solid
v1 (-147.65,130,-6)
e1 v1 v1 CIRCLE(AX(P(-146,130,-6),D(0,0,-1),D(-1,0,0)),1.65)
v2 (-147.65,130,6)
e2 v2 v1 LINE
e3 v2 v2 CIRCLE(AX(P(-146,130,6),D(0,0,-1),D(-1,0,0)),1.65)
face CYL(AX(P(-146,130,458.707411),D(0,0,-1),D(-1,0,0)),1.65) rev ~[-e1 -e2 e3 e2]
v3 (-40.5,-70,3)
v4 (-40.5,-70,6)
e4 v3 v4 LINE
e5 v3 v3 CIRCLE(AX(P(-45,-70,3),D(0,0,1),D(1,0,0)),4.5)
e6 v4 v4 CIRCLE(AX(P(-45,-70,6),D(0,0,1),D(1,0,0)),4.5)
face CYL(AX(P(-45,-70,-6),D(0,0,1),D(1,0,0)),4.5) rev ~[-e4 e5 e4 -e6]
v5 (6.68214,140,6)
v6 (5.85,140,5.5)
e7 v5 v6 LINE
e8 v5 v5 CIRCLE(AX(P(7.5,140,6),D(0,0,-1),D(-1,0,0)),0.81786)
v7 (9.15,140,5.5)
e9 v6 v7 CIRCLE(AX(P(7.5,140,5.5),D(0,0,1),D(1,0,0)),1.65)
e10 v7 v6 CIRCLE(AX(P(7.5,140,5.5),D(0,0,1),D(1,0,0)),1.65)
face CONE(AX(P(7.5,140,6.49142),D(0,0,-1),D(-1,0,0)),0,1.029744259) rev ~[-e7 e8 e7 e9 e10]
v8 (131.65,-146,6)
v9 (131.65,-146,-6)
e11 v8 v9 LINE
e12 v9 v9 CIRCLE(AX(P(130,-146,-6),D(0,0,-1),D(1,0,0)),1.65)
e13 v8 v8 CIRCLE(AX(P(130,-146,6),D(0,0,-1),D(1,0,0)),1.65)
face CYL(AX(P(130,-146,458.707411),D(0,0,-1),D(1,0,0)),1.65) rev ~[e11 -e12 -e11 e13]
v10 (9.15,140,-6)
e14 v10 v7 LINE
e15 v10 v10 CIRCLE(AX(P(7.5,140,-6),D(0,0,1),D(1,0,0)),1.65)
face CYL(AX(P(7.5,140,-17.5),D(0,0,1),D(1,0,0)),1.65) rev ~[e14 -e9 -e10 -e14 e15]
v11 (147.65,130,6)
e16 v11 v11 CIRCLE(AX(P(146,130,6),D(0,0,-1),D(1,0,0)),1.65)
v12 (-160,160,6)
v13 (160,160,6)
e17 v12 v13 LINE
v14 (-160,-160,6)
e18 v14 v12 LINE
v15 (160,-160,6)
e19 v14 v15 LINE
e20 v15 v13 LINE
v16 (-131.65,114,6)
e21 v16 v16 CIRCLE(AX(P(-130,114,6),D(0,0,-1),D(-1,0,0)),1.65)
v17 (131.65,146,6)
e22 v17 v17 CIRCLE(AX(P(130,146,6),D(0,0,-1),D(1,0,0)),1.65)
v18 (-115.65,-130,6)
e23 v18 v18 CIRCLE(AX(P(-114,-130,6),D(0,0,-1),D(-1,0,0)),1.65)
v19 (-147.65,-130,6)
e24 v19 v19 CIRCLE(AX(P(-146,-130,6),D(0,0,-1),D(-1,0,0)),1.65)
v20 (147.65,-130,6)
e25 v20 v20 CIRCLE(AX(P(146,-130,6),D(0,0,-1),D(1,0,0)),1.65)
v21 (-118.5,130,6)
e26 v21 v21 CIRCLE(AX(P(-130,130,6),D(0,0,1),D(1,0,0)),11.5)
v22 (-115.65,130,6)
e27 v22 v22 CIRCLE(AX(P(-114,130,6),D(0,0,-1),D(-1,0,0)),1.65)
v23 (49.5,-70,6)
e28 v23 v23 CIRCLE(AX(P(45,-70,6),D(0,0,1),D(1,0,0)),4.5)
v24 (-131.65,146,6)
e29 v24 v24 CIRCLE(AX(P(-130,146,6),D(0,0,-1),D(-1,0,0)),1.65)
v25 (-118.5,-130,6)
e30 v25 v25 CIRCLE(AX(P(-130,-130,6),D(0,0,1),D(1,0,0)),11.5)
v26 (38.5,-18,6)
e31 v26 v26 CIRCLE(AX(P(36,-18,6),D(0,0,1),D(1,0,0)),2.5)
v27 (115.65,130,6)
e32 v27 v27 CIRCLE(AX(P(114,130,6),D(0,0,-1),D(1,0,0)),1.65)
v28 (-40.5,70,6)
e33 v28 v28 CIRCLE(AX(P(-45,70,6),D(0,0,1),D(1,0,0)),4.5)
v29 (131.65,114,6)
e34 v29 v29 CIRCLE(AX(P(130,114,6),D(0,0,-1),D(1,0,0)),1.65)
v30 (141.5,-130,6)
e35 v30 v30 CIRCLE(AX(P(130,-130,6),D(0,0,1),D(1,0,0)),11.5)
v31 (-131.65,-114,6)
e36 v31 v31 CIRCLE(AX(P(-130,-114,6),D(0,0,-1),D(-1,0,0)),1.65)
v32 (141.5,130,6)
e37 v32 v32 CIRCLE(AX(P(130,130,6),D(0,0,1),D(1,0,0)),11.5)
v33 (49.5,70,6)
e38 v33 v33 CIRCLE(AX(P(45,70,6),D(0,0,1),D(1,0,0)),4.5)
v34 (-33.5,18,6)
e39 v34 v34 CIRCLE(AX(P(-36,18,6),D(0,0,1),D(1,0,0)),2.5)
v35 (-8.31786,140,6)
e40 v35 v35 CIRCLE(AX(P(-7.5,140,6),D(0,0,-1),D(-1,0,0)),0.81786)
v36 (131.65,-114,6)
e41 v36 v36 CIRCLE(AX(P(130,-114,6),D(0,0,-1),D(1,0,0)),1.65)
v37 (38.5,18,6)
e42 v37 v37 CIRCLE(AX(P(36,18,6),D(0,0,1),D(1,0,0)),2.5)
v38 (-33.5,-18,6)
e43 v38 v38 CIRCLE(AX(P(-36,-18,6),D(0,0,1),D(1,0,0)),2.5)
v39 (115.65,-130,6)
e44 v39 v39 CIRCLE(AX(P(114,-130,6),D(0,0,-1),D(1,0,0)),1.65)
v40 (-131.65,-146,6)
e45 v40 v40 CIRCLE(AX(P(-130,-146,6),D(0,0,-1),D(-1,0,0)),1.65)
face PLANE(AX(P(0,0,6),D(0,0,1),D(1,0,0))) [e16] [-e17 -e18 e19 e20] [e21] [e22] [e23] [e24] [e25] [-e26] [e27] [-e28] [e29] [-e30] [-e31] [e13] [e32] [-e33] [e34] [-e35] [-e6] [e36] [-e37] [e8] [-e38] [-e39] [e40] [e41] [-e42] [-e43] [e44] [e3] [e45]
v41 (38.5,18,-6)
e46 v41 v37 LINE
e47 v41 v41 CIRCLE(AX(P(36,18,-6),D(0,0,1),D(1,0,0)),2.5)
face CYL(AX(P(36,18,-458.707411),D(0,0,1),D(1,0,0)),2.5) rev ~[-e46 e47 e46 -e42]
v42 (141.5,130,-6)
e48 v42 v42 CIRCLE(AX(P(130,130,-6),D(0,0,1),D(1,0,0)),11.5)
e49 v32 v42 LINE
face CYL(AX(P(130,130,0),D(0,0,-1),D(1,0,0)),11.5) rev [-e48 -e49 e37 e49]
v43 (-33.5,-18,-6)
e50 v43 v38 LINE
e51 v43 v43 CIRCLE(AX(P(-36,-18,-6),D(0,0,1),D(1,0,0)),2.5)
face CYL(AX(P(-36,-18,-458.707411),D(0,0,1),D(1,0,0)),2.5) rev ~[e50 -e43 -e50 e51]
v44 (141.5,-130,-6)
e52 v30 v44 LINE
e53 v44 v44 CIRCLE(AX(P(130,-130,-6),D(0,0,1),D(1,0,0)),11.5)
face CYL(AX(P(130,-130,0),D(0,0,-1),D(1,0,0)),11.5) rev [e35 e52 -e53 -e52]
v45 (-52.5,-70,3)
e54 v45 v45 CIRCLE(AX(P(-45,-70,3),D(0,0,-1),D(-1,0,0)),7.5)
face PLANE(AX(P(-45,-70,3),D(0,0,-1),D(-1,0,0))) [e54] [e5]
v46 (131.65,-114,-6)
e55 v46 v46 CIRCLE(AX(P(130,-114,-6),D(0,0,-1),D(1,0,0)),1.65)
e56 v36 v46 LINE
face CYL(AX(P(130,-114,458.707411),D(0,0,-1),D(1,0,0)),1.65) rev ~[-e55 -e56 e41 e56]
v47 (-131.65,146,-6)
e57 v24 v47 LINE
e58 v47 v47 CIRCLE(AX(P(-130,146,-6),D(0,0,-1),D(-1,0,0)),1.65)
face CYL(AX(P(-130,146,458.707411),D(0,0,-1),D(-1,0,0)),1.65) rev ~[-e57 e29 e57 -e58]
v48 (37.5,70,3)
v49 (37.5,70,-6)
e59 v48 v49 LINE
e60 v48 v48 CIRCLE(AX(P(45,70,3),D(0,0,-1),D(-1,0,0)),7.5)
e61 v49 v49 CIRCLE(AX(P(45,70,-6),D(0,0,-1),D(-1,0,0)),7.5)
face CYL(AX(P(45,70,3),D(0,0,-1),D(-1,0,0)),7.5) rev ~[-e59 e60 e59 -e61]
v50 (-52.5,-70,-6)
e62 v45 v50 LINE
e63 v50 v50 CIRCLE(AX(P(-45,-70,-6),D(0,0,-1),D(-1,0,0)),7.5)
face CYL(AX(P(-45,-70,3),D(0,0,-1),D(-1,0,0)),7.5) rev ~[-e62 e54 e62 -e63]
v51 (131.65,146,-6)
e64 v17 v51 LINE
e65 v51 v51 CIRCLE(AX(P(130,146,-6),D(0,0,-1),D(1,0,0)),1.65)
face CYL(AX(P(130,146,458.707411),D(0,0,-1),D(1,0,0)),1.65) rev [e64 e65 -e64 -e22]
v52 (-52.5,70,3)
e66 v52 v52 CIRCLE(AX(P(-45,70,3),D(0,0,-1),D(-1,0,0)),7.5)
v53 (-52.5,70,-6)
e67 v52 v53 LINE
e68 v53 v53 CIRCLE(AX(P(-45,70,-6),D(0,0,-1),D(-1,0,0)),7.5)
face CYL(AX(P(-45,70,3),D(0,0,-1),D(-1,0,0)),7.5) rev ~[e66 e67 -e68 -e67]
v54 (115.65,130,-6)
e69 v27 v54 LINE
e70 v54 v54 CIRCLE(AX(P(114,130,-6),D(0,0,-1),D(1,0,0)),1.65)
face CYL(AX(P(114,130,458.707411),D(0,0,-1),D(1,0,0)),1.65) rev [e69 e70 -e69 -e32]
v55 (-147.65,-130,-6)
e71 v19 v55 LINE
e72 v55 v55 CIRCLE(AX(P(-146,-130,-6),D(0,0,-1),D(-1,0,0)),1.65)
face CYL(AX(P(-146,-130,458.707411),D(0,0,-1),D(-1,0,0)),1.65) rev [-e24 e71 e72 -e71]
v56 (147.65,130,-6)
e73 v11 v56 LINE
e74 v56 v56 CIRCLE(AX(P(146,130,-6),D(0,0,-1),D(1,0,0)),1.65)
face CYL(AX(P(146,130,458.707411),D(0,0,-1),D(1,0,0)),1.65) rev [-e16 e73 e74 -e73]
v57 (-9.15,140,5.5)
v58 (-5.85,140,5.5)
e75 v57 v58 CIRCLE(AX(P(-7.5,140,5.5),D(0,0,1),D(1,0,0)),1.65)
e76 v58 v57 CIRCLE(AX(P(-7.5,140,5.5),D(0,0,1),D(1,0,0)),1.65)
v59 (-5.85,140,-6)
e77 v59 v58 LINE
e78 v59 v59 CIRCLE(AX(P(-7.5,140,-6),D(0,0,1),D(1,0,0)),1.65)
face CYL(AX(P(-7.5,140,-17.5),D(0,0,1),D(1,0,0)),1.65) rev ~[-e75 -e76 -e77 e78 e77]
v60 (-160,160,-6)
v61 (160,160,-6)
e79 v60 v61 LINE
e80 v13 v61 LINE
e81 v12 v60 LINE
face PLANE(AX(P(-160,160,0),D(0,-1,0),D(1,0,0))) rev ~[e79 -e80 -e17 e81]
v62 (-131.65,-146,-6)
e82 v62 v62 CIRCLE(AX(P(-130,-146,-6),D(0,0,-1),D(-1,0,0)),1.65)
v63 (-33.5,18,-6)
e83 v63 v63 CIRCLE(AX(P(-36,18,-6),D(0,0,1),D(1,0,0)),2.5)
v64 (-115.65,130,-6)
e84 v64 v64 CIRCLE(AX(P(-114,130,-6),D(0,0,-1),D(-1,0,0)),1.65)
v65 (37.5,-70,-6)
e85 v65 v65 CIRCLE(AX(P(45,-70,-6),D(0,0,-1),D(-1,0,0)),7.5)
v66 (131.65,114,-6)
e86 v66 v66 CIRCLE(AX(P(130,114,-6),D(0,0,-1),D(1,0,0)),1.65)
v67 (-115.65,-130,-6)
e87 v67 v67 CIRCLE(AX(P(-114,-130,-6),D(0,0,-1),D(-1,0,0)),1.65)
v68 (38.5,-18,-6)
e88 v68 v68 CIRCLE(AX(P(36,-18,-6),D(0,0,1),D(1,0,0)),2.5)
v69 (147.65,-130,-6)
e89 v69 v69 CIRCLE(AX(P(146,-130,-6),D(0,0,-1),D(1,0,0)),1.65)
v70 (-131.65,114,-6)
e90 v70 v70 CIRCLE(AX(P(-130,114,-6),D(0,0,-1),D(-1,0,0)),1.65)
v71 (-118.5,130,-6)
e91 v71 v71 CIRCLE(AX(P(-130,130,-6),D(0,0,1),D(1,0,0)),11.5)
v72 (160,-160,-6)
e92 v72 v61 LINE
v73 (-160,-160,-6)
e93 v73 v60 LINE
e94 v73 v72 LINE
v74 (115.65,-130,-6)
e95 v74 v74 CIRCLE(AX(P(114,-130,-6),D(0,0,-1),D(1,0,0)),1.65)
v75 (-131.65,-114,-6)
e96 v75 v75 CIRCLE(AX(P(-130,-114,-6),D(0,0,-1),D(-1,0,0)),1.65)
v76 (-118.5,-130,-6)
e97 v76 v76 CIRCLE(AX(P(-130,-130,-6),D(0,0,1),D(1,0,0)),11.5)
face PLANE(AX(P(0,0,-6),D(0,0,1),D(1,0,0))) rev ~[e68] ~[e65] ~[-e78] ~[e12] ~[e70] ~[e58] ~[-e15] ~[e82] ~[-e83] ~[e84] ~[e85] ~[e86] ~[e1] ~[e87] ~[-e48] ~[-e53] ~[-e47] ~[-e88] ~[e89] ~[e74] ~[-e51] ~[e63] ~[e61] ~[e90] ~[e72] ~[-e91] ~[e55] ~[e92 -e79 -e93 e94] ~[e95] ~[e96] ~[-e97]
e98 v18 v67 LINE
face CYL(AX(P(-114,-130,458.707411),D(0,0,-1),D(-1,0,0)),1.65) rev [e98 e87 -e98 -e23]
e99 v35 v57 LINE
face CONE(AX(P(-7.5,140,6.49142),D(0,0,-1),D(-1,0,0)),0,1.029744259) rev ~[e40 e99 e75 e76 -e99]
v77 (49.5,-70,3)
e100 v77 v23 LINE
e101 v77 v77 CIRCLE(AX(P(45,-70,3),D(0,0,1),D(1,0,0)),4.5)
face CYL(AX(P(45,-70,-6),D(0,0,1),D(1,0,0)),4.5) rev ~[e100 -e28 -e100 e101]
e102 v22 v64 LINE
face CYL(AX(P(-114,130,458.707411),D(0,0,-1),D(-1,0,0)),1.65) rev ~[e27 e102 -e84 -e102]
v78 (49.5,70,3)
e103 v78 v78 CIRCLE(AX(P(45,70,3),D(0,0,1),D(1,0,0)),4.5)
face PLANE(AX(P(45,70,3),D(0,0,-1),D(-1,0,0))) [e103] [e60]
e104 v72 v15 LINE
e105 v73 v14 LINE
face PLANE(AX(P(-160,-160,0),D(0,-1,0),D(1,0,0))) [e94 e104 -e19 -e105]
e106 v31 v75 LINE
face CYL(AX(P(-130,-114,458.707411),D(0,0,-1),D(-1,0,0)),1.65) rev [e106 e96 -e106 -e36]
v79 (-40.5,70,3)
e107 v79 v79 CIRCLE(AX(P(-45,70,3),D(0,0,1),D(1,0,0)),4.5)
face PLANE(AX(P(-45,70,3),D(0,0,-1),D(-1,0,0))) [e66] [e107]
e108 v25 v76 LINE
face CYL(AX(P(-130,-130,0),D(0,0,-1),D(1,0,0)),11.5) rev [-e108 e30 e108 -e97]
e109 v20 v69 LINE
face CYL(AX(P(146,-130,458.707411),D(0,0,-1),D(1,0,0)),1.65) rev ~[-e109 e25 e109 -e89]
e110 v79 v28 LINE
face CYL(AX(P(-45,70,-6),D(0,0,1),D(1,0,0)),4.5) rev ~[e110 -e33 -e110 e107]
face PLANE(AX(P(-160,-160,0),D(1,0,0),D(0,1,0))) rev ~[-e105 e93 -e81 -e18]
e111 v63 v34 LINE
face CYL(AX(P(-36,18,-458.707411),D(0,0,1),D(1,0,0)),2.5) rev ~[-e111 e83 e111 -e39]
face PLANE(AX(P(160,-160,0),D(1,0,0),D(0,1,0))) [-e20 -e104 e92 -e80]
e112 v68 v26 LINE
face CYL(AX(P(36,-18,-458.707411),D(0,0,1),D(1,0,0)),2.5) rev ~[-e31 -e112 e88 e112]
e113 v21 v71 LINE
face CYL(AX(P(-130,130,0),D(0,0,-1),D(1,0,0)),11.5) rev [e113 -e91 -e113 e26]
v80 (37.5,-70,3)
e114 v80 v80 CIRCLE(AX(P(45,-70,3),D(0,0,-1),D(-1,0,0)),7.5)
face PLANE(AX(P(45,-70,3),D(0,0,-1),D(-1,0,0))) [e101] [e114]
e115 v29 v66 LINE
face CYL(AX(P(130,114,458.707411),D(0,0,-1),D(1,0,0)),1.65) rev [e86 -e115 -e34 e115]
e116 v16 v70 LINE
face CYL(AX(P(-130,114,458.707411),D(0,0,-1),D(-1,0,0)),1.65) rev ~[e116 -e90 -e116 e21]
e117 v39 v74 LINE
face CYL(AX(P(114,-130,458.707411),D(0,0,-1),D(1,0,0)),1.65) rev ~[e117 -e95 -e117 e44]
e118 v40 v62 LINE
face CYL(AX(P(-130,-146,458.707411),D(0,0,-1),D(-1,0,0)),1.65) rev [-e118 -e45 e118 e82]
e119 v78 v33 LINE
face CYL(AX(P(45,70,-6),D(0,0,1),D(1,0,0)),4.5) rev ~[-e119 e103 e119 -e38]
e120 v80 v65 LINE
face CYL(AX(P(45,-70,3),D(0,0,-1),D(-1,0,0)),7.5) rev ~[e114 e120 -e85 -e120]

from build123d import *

# Parameters (mm, degrees)
SKETCH_1_W                = 320
SKETCH_1_H                = 320
SKETCH_1_R                = 11.5
EXTRUDE_1_DEPTH           = 6
HOLE_WIZARD_M6_1_D        = 5
HOLE_WIZARD_1_D           = 9
HOLE_WIZARD_1_CBORE_D     = 15
HOLE_WIZARD_1_CBORE_DEPTH = 9
HOLE_WIZARD_M4_2_D        = 3.3
MIRROR_2_COPY_1_D         = 3.3
HOLE_WIZARD_M4_1_D        = 3.3
HOLE_WIZARD_M4_1_DEPTH    = 11.5
HOLE_WIZARD_M4_1_TIP      = 0.991420021


with BuildPart() as part:
    # 草图1 → 凸台-拉伸1 (new, symmetric)
    with BuildSketch(Plane.XY):
        Rectangle(SKETCH_1_W, SKETCH_1_H)
        with Locations((-130, 130)):
            Circle(SKETCH_1_R, mode=Mode.SUBTRACT)
        with Locations((130, 130)):
            Circle(SKETCH_1_R, mode=Mode.SUBTRACT)
        with Locations((130, -130)):
            Circle(SKETCH_1_R, mode=Mode.SUBTRACT)
        with Locations((-130, -130)):
            Circle(SKETCH_1_R, mode=Mode.SUBTRACT)
    extrude(amount=EXTRUDE_1_DEPTH, both=True)

    # M6 螺纹孔1 (through all)
    with Locations(Plane(origin=(0, 0, -6), x_dir=(-1, 0, 0), z_dir=(0, 0, -1))):
        with Locations((-36, 18), (-36, -18), (36, -18), (36, 18)):
            Hole(HOLE_WIZARD_M6_1_D / 2)

    # 打孔尺寸(%根据)内六角圆柱头螺钉的类型1 (through all)
    with Locations(Plane(origin=(0, 0, -6), x_dir=(-1, 0, 0), z_dir=(0, 0, -1))):
        with Locations((-45, 70), (45, 70), (45, -70), (-45, -70)):
            CounterBoreHole(HOLE_WIZARD_1_D / 2, HOLE_WIZARD_1_CBORE_D / 2, HOLE_WIZARD_1_CBORE_DEPTH)

    # M4 螺纹孔2 (through all)
    with Locations(Plane.XY.offset(6)):
        with Locations((-130, 146), (-114, 130), (-130, 114), (-146, 130)):
            hole_wizard_m4_2 = Hole(HOLE_WIZARD_M4_2_D / 2)

    # 镜向1: M4 螺纹孔2 across plane
    add(hole_wizard_m4_2.mirror(Plane.ZX), mode=Mode.SUBTRACT)

    # 镜向2: M4 螺纹孔2 across plane
    add(hole_wizard_m4_2.mirror(Plane(origin=(0, 0, 0), x_dir=(0, 0, 1), z_dir=(1, 0, 0))), mode=Mode.SUBTRACT)

    # 镜向2 copy 1 (through all)
    with Locations(Plane(origin=(0, 0, 6), x_dir=(-1, 0, 0), z_dir=(0, 0, 1))):
        with Locations((-130, 146), (-114, 130), (-130, 114), (-146, 130)):
            Hole(MIRROR_2_COPY_1_D / 2)

    # M4 螺纹孔1
    with Locations(Plane(origin=(0, 0, -6), x_dir=(-1, 0, 0), z_dir=(0, 0, -1))):
        with Locations((-7.5, 140), (7.5, 140)):
            Hole(HOLE_WIZARD_M4_1_D / 2, depth=HOLE_WIZARD_M4_1_DEPTH)
            with Locations((0, 0, -(HOLE_WIZARD_M4_1_DEPTH + HOLE_WIZARD_M4_1_TIP / 2))):  # 118° drill point
                Cone(0, HOLE_WIZARD_M4_1_D / 2, HOLE_WIZARD_M4_1_TIP, mode=Mode.SUBTRACT)


solid = part.part
